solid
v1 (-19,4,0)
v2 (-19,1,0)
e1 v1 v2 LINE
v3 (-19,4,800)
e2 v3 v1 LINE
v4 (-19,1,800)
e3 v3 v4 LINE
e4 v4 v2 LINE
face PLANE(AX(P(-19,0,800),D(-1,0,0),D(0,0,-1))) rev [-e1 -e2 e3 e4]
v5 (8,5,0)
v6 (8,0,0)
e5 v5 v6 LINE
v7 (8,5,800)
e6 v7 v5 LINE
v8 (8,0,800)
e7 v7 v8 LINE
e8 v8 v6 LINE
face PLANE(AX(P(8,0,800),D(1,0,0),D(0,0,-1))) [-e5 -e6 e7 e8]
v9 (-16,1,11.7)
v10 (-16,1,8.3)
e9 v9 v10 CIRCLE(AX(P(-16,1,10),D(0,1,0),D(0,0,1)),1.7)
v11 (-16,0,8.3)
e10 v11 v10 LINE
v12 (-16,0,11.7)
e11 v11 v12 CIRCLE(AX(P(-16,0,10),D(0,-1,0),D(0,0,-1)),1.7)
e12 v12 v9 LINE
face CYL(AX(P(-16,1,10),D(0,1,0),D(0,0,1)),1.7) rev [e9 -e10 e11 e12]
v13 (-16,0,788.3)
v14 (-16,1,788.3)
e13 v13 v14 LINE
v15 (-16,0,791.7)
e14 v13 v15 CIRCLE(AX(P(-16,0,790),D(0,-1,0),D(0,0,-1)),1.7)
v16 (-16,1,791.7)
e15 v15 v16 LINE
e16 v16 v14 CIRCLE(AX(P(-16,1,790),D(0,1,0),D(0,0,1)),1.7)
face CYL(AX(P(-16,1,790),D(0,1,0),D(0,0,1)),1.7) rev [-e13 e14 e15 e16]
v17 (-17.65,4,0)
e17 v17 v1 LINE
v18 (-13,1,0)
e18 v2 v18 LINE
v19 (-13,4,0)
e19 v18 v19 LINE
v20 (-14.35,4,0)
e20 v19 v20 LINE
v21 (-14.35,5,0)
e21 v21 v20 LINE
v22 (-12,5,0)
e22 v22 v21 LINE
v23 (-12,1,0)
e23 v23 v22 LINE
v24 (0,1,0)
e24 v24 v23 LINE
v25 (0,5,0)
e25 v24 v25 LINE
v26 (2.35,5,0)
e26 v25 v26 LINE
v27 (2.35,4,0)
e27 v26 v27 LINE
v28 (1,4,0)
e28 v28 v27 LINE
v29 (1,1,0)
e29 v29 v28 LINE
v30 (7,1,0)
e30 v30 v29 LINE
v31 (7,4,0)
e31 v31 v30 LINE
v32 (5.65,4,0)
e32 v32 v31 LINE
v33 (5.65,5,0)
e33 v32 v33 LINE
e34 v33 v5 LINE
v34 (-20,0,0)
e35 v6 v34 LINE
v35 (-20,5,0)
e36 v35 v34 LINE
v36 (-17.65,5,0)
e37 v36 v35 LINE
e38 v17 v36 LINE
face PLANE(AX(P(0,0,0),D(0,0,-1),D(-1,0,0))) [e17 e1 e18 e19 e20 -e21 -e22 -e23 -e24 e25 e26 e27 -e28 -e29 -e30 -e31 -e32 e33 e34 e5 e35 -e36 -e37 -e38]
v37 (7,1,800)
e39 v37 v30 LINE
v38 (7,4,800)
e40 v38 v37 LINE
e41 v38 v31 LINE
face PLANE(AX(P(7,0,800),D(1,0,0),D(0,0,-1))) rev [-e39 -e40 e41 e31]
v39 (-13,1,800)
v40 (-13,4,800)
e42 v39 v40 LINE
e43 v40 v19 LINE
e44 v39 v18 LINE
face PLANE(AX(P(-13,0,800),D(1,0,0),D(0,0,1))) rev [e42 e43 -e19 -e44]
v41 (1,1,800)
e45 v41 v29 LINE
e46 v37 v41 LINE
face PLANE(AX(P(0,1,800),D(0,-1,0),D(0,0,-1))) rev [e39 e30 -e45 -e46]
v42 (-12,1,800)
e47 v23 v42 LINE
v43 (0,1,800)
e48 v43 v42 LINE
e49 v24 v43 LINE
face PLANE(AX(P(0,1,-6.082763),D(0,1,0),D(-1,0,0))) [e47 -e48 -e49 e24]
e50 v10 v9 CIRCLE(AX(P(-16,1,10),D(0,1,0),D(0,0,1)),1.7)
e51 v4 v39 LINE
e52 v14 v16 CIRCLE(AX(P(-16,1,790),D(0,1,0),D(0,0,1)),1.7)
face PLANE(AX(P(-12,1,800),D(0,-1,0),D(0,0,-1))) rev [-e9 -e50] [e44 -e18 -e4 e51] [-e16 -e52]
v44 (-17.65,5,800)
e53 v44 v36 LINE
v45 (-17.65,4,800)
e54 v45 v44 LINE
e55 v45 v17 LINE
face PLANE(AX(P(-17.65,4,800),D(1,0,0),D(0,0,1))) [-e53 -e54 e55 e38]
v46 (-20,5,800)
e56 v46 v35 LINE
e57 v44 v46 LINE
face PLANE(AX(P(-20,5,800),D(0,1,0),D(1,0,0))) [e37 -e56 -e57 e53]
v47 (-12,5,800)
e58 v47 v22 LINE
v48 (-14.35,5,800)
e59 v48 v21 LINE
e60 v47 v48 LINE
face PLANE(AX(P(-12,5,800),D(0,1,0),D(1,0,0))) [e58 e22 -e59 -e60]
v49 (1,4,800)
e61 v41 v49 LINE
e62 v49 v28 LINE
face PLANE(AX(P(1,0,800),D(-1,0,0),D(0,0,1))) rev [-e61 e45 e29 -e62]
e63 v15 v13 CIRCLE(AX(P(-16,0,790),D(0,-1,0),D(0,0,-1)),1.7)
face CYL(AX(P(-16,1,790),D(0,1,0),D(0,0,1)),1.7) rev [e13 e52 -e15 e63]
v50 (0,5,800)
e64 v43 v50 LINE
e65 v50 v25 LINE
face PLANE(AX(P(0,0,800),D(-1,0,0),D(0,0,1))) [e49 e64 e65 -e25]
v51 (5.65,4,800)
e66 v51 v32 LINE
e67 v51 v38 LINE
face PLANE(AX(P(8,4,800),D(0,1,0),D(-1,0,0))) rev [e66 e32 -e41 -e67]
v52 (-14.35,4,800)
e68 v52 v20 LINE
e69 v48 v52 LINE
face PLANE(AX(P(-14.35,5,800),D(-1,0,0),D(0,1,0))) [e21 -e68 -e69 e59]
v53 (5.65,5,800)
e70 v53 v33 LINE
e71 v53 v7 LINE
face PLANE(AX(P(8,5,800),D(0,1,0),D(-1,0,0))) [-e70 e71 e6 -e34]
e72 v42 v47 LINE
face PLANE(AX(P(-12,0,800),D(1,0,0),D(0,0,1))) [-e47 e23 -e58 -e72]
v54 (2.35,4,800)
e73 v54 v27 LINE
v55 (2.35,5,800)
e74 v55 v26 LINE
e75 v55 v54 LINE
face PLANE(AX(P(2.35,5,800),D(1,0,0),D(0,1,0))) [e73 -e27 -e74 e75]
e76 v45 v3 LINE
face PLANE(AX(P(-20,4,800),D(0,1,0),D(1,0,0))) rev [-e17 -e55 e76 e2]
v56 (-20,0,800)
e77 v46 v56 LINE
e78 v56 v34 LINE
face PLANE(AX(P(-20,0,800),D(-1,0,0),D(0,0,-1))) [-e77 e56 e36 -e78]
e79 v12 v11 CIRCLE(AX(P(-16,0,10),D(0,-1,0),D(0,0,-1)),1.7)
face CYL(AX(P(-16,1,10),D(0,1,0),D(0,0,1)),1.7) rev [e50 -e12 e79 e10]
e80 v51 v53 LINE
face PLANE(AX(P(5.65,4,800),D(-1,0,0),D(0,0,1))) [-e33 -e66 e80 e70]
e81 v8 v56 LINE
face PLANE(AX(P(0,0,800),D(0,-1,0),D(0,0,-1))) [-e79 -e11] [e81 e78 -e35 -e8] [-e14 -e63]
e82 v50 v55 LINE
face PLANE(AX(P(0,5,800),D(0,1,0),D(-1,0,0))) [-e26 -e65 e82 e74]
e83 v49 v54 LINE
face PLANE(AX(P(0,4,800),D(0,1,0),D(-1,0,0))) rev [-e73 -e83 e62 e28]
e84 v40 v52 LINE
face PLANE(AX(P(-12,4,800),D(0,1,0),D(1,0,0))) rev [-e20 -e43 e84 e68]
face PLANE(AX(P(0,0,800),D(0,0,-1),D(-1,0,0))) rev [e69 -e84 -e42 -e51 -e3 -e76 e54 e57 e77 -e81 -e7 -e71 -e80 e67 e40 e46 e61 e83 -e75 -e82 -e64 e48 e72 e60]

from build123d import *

# Parameters (mm, degrees)
EXTRUDE_1_DEPTH        = 800
SKETCH_2_W             = 6
SKETCH_2_H             = 1
EXTRUDE_2_DEPTH        = 800
HOLE_WIZARD_M3_1_D     = 3.4
HOLE_WIZARD_M3_1_DEPTH = 1


with BuildPart() as part:
    # 草图1 → 拉伸-薄壁1 (new body)
    with BuildSketch(Plane.XY):
        Polygon((2.35, 5), (0, 5), (0, 0), (8, 0), (8, 5), (5.65, 5), (5.65, 4), (7, 4), (7, 1), (1, 1), (1, 4), (2.35, 4), align=None)
    extrude(amount=EXTRUDE_1_DEPTH)

    # 草图2 → 拉伸-薄壁2 (add)
    with BuildSketch(Plane.XY.offset(800)):
        with Locations((-3, 0.5)):
            Rectangle(SKETCH_2_W, SKETCH_2_H)
    extrude(amount=-EXTRUDE_2_DEPTH)

    # 镜向1: part across plane


with BuildPart() as part_1:
    add(part.part)
    add(part.part.mirror(Plane(origin=(-6, 0, -6.08276253), x_dir=(0, 0, 1), z_dir=(1, 0, 0))))

    # M3 间隙孔1
    with Locations(Plane(origin=(0, 1, 0), x_dir=(1, 0, 0), z_dir=(0, 1, 0))):
        with Locations((-16, -10), (-16, -790)):
            Hole(HOLE_WIZARD_M3_1_D / 2, depth=HOLE_WIZARD_M3_1_DEPTH)


solid = part_1.part
